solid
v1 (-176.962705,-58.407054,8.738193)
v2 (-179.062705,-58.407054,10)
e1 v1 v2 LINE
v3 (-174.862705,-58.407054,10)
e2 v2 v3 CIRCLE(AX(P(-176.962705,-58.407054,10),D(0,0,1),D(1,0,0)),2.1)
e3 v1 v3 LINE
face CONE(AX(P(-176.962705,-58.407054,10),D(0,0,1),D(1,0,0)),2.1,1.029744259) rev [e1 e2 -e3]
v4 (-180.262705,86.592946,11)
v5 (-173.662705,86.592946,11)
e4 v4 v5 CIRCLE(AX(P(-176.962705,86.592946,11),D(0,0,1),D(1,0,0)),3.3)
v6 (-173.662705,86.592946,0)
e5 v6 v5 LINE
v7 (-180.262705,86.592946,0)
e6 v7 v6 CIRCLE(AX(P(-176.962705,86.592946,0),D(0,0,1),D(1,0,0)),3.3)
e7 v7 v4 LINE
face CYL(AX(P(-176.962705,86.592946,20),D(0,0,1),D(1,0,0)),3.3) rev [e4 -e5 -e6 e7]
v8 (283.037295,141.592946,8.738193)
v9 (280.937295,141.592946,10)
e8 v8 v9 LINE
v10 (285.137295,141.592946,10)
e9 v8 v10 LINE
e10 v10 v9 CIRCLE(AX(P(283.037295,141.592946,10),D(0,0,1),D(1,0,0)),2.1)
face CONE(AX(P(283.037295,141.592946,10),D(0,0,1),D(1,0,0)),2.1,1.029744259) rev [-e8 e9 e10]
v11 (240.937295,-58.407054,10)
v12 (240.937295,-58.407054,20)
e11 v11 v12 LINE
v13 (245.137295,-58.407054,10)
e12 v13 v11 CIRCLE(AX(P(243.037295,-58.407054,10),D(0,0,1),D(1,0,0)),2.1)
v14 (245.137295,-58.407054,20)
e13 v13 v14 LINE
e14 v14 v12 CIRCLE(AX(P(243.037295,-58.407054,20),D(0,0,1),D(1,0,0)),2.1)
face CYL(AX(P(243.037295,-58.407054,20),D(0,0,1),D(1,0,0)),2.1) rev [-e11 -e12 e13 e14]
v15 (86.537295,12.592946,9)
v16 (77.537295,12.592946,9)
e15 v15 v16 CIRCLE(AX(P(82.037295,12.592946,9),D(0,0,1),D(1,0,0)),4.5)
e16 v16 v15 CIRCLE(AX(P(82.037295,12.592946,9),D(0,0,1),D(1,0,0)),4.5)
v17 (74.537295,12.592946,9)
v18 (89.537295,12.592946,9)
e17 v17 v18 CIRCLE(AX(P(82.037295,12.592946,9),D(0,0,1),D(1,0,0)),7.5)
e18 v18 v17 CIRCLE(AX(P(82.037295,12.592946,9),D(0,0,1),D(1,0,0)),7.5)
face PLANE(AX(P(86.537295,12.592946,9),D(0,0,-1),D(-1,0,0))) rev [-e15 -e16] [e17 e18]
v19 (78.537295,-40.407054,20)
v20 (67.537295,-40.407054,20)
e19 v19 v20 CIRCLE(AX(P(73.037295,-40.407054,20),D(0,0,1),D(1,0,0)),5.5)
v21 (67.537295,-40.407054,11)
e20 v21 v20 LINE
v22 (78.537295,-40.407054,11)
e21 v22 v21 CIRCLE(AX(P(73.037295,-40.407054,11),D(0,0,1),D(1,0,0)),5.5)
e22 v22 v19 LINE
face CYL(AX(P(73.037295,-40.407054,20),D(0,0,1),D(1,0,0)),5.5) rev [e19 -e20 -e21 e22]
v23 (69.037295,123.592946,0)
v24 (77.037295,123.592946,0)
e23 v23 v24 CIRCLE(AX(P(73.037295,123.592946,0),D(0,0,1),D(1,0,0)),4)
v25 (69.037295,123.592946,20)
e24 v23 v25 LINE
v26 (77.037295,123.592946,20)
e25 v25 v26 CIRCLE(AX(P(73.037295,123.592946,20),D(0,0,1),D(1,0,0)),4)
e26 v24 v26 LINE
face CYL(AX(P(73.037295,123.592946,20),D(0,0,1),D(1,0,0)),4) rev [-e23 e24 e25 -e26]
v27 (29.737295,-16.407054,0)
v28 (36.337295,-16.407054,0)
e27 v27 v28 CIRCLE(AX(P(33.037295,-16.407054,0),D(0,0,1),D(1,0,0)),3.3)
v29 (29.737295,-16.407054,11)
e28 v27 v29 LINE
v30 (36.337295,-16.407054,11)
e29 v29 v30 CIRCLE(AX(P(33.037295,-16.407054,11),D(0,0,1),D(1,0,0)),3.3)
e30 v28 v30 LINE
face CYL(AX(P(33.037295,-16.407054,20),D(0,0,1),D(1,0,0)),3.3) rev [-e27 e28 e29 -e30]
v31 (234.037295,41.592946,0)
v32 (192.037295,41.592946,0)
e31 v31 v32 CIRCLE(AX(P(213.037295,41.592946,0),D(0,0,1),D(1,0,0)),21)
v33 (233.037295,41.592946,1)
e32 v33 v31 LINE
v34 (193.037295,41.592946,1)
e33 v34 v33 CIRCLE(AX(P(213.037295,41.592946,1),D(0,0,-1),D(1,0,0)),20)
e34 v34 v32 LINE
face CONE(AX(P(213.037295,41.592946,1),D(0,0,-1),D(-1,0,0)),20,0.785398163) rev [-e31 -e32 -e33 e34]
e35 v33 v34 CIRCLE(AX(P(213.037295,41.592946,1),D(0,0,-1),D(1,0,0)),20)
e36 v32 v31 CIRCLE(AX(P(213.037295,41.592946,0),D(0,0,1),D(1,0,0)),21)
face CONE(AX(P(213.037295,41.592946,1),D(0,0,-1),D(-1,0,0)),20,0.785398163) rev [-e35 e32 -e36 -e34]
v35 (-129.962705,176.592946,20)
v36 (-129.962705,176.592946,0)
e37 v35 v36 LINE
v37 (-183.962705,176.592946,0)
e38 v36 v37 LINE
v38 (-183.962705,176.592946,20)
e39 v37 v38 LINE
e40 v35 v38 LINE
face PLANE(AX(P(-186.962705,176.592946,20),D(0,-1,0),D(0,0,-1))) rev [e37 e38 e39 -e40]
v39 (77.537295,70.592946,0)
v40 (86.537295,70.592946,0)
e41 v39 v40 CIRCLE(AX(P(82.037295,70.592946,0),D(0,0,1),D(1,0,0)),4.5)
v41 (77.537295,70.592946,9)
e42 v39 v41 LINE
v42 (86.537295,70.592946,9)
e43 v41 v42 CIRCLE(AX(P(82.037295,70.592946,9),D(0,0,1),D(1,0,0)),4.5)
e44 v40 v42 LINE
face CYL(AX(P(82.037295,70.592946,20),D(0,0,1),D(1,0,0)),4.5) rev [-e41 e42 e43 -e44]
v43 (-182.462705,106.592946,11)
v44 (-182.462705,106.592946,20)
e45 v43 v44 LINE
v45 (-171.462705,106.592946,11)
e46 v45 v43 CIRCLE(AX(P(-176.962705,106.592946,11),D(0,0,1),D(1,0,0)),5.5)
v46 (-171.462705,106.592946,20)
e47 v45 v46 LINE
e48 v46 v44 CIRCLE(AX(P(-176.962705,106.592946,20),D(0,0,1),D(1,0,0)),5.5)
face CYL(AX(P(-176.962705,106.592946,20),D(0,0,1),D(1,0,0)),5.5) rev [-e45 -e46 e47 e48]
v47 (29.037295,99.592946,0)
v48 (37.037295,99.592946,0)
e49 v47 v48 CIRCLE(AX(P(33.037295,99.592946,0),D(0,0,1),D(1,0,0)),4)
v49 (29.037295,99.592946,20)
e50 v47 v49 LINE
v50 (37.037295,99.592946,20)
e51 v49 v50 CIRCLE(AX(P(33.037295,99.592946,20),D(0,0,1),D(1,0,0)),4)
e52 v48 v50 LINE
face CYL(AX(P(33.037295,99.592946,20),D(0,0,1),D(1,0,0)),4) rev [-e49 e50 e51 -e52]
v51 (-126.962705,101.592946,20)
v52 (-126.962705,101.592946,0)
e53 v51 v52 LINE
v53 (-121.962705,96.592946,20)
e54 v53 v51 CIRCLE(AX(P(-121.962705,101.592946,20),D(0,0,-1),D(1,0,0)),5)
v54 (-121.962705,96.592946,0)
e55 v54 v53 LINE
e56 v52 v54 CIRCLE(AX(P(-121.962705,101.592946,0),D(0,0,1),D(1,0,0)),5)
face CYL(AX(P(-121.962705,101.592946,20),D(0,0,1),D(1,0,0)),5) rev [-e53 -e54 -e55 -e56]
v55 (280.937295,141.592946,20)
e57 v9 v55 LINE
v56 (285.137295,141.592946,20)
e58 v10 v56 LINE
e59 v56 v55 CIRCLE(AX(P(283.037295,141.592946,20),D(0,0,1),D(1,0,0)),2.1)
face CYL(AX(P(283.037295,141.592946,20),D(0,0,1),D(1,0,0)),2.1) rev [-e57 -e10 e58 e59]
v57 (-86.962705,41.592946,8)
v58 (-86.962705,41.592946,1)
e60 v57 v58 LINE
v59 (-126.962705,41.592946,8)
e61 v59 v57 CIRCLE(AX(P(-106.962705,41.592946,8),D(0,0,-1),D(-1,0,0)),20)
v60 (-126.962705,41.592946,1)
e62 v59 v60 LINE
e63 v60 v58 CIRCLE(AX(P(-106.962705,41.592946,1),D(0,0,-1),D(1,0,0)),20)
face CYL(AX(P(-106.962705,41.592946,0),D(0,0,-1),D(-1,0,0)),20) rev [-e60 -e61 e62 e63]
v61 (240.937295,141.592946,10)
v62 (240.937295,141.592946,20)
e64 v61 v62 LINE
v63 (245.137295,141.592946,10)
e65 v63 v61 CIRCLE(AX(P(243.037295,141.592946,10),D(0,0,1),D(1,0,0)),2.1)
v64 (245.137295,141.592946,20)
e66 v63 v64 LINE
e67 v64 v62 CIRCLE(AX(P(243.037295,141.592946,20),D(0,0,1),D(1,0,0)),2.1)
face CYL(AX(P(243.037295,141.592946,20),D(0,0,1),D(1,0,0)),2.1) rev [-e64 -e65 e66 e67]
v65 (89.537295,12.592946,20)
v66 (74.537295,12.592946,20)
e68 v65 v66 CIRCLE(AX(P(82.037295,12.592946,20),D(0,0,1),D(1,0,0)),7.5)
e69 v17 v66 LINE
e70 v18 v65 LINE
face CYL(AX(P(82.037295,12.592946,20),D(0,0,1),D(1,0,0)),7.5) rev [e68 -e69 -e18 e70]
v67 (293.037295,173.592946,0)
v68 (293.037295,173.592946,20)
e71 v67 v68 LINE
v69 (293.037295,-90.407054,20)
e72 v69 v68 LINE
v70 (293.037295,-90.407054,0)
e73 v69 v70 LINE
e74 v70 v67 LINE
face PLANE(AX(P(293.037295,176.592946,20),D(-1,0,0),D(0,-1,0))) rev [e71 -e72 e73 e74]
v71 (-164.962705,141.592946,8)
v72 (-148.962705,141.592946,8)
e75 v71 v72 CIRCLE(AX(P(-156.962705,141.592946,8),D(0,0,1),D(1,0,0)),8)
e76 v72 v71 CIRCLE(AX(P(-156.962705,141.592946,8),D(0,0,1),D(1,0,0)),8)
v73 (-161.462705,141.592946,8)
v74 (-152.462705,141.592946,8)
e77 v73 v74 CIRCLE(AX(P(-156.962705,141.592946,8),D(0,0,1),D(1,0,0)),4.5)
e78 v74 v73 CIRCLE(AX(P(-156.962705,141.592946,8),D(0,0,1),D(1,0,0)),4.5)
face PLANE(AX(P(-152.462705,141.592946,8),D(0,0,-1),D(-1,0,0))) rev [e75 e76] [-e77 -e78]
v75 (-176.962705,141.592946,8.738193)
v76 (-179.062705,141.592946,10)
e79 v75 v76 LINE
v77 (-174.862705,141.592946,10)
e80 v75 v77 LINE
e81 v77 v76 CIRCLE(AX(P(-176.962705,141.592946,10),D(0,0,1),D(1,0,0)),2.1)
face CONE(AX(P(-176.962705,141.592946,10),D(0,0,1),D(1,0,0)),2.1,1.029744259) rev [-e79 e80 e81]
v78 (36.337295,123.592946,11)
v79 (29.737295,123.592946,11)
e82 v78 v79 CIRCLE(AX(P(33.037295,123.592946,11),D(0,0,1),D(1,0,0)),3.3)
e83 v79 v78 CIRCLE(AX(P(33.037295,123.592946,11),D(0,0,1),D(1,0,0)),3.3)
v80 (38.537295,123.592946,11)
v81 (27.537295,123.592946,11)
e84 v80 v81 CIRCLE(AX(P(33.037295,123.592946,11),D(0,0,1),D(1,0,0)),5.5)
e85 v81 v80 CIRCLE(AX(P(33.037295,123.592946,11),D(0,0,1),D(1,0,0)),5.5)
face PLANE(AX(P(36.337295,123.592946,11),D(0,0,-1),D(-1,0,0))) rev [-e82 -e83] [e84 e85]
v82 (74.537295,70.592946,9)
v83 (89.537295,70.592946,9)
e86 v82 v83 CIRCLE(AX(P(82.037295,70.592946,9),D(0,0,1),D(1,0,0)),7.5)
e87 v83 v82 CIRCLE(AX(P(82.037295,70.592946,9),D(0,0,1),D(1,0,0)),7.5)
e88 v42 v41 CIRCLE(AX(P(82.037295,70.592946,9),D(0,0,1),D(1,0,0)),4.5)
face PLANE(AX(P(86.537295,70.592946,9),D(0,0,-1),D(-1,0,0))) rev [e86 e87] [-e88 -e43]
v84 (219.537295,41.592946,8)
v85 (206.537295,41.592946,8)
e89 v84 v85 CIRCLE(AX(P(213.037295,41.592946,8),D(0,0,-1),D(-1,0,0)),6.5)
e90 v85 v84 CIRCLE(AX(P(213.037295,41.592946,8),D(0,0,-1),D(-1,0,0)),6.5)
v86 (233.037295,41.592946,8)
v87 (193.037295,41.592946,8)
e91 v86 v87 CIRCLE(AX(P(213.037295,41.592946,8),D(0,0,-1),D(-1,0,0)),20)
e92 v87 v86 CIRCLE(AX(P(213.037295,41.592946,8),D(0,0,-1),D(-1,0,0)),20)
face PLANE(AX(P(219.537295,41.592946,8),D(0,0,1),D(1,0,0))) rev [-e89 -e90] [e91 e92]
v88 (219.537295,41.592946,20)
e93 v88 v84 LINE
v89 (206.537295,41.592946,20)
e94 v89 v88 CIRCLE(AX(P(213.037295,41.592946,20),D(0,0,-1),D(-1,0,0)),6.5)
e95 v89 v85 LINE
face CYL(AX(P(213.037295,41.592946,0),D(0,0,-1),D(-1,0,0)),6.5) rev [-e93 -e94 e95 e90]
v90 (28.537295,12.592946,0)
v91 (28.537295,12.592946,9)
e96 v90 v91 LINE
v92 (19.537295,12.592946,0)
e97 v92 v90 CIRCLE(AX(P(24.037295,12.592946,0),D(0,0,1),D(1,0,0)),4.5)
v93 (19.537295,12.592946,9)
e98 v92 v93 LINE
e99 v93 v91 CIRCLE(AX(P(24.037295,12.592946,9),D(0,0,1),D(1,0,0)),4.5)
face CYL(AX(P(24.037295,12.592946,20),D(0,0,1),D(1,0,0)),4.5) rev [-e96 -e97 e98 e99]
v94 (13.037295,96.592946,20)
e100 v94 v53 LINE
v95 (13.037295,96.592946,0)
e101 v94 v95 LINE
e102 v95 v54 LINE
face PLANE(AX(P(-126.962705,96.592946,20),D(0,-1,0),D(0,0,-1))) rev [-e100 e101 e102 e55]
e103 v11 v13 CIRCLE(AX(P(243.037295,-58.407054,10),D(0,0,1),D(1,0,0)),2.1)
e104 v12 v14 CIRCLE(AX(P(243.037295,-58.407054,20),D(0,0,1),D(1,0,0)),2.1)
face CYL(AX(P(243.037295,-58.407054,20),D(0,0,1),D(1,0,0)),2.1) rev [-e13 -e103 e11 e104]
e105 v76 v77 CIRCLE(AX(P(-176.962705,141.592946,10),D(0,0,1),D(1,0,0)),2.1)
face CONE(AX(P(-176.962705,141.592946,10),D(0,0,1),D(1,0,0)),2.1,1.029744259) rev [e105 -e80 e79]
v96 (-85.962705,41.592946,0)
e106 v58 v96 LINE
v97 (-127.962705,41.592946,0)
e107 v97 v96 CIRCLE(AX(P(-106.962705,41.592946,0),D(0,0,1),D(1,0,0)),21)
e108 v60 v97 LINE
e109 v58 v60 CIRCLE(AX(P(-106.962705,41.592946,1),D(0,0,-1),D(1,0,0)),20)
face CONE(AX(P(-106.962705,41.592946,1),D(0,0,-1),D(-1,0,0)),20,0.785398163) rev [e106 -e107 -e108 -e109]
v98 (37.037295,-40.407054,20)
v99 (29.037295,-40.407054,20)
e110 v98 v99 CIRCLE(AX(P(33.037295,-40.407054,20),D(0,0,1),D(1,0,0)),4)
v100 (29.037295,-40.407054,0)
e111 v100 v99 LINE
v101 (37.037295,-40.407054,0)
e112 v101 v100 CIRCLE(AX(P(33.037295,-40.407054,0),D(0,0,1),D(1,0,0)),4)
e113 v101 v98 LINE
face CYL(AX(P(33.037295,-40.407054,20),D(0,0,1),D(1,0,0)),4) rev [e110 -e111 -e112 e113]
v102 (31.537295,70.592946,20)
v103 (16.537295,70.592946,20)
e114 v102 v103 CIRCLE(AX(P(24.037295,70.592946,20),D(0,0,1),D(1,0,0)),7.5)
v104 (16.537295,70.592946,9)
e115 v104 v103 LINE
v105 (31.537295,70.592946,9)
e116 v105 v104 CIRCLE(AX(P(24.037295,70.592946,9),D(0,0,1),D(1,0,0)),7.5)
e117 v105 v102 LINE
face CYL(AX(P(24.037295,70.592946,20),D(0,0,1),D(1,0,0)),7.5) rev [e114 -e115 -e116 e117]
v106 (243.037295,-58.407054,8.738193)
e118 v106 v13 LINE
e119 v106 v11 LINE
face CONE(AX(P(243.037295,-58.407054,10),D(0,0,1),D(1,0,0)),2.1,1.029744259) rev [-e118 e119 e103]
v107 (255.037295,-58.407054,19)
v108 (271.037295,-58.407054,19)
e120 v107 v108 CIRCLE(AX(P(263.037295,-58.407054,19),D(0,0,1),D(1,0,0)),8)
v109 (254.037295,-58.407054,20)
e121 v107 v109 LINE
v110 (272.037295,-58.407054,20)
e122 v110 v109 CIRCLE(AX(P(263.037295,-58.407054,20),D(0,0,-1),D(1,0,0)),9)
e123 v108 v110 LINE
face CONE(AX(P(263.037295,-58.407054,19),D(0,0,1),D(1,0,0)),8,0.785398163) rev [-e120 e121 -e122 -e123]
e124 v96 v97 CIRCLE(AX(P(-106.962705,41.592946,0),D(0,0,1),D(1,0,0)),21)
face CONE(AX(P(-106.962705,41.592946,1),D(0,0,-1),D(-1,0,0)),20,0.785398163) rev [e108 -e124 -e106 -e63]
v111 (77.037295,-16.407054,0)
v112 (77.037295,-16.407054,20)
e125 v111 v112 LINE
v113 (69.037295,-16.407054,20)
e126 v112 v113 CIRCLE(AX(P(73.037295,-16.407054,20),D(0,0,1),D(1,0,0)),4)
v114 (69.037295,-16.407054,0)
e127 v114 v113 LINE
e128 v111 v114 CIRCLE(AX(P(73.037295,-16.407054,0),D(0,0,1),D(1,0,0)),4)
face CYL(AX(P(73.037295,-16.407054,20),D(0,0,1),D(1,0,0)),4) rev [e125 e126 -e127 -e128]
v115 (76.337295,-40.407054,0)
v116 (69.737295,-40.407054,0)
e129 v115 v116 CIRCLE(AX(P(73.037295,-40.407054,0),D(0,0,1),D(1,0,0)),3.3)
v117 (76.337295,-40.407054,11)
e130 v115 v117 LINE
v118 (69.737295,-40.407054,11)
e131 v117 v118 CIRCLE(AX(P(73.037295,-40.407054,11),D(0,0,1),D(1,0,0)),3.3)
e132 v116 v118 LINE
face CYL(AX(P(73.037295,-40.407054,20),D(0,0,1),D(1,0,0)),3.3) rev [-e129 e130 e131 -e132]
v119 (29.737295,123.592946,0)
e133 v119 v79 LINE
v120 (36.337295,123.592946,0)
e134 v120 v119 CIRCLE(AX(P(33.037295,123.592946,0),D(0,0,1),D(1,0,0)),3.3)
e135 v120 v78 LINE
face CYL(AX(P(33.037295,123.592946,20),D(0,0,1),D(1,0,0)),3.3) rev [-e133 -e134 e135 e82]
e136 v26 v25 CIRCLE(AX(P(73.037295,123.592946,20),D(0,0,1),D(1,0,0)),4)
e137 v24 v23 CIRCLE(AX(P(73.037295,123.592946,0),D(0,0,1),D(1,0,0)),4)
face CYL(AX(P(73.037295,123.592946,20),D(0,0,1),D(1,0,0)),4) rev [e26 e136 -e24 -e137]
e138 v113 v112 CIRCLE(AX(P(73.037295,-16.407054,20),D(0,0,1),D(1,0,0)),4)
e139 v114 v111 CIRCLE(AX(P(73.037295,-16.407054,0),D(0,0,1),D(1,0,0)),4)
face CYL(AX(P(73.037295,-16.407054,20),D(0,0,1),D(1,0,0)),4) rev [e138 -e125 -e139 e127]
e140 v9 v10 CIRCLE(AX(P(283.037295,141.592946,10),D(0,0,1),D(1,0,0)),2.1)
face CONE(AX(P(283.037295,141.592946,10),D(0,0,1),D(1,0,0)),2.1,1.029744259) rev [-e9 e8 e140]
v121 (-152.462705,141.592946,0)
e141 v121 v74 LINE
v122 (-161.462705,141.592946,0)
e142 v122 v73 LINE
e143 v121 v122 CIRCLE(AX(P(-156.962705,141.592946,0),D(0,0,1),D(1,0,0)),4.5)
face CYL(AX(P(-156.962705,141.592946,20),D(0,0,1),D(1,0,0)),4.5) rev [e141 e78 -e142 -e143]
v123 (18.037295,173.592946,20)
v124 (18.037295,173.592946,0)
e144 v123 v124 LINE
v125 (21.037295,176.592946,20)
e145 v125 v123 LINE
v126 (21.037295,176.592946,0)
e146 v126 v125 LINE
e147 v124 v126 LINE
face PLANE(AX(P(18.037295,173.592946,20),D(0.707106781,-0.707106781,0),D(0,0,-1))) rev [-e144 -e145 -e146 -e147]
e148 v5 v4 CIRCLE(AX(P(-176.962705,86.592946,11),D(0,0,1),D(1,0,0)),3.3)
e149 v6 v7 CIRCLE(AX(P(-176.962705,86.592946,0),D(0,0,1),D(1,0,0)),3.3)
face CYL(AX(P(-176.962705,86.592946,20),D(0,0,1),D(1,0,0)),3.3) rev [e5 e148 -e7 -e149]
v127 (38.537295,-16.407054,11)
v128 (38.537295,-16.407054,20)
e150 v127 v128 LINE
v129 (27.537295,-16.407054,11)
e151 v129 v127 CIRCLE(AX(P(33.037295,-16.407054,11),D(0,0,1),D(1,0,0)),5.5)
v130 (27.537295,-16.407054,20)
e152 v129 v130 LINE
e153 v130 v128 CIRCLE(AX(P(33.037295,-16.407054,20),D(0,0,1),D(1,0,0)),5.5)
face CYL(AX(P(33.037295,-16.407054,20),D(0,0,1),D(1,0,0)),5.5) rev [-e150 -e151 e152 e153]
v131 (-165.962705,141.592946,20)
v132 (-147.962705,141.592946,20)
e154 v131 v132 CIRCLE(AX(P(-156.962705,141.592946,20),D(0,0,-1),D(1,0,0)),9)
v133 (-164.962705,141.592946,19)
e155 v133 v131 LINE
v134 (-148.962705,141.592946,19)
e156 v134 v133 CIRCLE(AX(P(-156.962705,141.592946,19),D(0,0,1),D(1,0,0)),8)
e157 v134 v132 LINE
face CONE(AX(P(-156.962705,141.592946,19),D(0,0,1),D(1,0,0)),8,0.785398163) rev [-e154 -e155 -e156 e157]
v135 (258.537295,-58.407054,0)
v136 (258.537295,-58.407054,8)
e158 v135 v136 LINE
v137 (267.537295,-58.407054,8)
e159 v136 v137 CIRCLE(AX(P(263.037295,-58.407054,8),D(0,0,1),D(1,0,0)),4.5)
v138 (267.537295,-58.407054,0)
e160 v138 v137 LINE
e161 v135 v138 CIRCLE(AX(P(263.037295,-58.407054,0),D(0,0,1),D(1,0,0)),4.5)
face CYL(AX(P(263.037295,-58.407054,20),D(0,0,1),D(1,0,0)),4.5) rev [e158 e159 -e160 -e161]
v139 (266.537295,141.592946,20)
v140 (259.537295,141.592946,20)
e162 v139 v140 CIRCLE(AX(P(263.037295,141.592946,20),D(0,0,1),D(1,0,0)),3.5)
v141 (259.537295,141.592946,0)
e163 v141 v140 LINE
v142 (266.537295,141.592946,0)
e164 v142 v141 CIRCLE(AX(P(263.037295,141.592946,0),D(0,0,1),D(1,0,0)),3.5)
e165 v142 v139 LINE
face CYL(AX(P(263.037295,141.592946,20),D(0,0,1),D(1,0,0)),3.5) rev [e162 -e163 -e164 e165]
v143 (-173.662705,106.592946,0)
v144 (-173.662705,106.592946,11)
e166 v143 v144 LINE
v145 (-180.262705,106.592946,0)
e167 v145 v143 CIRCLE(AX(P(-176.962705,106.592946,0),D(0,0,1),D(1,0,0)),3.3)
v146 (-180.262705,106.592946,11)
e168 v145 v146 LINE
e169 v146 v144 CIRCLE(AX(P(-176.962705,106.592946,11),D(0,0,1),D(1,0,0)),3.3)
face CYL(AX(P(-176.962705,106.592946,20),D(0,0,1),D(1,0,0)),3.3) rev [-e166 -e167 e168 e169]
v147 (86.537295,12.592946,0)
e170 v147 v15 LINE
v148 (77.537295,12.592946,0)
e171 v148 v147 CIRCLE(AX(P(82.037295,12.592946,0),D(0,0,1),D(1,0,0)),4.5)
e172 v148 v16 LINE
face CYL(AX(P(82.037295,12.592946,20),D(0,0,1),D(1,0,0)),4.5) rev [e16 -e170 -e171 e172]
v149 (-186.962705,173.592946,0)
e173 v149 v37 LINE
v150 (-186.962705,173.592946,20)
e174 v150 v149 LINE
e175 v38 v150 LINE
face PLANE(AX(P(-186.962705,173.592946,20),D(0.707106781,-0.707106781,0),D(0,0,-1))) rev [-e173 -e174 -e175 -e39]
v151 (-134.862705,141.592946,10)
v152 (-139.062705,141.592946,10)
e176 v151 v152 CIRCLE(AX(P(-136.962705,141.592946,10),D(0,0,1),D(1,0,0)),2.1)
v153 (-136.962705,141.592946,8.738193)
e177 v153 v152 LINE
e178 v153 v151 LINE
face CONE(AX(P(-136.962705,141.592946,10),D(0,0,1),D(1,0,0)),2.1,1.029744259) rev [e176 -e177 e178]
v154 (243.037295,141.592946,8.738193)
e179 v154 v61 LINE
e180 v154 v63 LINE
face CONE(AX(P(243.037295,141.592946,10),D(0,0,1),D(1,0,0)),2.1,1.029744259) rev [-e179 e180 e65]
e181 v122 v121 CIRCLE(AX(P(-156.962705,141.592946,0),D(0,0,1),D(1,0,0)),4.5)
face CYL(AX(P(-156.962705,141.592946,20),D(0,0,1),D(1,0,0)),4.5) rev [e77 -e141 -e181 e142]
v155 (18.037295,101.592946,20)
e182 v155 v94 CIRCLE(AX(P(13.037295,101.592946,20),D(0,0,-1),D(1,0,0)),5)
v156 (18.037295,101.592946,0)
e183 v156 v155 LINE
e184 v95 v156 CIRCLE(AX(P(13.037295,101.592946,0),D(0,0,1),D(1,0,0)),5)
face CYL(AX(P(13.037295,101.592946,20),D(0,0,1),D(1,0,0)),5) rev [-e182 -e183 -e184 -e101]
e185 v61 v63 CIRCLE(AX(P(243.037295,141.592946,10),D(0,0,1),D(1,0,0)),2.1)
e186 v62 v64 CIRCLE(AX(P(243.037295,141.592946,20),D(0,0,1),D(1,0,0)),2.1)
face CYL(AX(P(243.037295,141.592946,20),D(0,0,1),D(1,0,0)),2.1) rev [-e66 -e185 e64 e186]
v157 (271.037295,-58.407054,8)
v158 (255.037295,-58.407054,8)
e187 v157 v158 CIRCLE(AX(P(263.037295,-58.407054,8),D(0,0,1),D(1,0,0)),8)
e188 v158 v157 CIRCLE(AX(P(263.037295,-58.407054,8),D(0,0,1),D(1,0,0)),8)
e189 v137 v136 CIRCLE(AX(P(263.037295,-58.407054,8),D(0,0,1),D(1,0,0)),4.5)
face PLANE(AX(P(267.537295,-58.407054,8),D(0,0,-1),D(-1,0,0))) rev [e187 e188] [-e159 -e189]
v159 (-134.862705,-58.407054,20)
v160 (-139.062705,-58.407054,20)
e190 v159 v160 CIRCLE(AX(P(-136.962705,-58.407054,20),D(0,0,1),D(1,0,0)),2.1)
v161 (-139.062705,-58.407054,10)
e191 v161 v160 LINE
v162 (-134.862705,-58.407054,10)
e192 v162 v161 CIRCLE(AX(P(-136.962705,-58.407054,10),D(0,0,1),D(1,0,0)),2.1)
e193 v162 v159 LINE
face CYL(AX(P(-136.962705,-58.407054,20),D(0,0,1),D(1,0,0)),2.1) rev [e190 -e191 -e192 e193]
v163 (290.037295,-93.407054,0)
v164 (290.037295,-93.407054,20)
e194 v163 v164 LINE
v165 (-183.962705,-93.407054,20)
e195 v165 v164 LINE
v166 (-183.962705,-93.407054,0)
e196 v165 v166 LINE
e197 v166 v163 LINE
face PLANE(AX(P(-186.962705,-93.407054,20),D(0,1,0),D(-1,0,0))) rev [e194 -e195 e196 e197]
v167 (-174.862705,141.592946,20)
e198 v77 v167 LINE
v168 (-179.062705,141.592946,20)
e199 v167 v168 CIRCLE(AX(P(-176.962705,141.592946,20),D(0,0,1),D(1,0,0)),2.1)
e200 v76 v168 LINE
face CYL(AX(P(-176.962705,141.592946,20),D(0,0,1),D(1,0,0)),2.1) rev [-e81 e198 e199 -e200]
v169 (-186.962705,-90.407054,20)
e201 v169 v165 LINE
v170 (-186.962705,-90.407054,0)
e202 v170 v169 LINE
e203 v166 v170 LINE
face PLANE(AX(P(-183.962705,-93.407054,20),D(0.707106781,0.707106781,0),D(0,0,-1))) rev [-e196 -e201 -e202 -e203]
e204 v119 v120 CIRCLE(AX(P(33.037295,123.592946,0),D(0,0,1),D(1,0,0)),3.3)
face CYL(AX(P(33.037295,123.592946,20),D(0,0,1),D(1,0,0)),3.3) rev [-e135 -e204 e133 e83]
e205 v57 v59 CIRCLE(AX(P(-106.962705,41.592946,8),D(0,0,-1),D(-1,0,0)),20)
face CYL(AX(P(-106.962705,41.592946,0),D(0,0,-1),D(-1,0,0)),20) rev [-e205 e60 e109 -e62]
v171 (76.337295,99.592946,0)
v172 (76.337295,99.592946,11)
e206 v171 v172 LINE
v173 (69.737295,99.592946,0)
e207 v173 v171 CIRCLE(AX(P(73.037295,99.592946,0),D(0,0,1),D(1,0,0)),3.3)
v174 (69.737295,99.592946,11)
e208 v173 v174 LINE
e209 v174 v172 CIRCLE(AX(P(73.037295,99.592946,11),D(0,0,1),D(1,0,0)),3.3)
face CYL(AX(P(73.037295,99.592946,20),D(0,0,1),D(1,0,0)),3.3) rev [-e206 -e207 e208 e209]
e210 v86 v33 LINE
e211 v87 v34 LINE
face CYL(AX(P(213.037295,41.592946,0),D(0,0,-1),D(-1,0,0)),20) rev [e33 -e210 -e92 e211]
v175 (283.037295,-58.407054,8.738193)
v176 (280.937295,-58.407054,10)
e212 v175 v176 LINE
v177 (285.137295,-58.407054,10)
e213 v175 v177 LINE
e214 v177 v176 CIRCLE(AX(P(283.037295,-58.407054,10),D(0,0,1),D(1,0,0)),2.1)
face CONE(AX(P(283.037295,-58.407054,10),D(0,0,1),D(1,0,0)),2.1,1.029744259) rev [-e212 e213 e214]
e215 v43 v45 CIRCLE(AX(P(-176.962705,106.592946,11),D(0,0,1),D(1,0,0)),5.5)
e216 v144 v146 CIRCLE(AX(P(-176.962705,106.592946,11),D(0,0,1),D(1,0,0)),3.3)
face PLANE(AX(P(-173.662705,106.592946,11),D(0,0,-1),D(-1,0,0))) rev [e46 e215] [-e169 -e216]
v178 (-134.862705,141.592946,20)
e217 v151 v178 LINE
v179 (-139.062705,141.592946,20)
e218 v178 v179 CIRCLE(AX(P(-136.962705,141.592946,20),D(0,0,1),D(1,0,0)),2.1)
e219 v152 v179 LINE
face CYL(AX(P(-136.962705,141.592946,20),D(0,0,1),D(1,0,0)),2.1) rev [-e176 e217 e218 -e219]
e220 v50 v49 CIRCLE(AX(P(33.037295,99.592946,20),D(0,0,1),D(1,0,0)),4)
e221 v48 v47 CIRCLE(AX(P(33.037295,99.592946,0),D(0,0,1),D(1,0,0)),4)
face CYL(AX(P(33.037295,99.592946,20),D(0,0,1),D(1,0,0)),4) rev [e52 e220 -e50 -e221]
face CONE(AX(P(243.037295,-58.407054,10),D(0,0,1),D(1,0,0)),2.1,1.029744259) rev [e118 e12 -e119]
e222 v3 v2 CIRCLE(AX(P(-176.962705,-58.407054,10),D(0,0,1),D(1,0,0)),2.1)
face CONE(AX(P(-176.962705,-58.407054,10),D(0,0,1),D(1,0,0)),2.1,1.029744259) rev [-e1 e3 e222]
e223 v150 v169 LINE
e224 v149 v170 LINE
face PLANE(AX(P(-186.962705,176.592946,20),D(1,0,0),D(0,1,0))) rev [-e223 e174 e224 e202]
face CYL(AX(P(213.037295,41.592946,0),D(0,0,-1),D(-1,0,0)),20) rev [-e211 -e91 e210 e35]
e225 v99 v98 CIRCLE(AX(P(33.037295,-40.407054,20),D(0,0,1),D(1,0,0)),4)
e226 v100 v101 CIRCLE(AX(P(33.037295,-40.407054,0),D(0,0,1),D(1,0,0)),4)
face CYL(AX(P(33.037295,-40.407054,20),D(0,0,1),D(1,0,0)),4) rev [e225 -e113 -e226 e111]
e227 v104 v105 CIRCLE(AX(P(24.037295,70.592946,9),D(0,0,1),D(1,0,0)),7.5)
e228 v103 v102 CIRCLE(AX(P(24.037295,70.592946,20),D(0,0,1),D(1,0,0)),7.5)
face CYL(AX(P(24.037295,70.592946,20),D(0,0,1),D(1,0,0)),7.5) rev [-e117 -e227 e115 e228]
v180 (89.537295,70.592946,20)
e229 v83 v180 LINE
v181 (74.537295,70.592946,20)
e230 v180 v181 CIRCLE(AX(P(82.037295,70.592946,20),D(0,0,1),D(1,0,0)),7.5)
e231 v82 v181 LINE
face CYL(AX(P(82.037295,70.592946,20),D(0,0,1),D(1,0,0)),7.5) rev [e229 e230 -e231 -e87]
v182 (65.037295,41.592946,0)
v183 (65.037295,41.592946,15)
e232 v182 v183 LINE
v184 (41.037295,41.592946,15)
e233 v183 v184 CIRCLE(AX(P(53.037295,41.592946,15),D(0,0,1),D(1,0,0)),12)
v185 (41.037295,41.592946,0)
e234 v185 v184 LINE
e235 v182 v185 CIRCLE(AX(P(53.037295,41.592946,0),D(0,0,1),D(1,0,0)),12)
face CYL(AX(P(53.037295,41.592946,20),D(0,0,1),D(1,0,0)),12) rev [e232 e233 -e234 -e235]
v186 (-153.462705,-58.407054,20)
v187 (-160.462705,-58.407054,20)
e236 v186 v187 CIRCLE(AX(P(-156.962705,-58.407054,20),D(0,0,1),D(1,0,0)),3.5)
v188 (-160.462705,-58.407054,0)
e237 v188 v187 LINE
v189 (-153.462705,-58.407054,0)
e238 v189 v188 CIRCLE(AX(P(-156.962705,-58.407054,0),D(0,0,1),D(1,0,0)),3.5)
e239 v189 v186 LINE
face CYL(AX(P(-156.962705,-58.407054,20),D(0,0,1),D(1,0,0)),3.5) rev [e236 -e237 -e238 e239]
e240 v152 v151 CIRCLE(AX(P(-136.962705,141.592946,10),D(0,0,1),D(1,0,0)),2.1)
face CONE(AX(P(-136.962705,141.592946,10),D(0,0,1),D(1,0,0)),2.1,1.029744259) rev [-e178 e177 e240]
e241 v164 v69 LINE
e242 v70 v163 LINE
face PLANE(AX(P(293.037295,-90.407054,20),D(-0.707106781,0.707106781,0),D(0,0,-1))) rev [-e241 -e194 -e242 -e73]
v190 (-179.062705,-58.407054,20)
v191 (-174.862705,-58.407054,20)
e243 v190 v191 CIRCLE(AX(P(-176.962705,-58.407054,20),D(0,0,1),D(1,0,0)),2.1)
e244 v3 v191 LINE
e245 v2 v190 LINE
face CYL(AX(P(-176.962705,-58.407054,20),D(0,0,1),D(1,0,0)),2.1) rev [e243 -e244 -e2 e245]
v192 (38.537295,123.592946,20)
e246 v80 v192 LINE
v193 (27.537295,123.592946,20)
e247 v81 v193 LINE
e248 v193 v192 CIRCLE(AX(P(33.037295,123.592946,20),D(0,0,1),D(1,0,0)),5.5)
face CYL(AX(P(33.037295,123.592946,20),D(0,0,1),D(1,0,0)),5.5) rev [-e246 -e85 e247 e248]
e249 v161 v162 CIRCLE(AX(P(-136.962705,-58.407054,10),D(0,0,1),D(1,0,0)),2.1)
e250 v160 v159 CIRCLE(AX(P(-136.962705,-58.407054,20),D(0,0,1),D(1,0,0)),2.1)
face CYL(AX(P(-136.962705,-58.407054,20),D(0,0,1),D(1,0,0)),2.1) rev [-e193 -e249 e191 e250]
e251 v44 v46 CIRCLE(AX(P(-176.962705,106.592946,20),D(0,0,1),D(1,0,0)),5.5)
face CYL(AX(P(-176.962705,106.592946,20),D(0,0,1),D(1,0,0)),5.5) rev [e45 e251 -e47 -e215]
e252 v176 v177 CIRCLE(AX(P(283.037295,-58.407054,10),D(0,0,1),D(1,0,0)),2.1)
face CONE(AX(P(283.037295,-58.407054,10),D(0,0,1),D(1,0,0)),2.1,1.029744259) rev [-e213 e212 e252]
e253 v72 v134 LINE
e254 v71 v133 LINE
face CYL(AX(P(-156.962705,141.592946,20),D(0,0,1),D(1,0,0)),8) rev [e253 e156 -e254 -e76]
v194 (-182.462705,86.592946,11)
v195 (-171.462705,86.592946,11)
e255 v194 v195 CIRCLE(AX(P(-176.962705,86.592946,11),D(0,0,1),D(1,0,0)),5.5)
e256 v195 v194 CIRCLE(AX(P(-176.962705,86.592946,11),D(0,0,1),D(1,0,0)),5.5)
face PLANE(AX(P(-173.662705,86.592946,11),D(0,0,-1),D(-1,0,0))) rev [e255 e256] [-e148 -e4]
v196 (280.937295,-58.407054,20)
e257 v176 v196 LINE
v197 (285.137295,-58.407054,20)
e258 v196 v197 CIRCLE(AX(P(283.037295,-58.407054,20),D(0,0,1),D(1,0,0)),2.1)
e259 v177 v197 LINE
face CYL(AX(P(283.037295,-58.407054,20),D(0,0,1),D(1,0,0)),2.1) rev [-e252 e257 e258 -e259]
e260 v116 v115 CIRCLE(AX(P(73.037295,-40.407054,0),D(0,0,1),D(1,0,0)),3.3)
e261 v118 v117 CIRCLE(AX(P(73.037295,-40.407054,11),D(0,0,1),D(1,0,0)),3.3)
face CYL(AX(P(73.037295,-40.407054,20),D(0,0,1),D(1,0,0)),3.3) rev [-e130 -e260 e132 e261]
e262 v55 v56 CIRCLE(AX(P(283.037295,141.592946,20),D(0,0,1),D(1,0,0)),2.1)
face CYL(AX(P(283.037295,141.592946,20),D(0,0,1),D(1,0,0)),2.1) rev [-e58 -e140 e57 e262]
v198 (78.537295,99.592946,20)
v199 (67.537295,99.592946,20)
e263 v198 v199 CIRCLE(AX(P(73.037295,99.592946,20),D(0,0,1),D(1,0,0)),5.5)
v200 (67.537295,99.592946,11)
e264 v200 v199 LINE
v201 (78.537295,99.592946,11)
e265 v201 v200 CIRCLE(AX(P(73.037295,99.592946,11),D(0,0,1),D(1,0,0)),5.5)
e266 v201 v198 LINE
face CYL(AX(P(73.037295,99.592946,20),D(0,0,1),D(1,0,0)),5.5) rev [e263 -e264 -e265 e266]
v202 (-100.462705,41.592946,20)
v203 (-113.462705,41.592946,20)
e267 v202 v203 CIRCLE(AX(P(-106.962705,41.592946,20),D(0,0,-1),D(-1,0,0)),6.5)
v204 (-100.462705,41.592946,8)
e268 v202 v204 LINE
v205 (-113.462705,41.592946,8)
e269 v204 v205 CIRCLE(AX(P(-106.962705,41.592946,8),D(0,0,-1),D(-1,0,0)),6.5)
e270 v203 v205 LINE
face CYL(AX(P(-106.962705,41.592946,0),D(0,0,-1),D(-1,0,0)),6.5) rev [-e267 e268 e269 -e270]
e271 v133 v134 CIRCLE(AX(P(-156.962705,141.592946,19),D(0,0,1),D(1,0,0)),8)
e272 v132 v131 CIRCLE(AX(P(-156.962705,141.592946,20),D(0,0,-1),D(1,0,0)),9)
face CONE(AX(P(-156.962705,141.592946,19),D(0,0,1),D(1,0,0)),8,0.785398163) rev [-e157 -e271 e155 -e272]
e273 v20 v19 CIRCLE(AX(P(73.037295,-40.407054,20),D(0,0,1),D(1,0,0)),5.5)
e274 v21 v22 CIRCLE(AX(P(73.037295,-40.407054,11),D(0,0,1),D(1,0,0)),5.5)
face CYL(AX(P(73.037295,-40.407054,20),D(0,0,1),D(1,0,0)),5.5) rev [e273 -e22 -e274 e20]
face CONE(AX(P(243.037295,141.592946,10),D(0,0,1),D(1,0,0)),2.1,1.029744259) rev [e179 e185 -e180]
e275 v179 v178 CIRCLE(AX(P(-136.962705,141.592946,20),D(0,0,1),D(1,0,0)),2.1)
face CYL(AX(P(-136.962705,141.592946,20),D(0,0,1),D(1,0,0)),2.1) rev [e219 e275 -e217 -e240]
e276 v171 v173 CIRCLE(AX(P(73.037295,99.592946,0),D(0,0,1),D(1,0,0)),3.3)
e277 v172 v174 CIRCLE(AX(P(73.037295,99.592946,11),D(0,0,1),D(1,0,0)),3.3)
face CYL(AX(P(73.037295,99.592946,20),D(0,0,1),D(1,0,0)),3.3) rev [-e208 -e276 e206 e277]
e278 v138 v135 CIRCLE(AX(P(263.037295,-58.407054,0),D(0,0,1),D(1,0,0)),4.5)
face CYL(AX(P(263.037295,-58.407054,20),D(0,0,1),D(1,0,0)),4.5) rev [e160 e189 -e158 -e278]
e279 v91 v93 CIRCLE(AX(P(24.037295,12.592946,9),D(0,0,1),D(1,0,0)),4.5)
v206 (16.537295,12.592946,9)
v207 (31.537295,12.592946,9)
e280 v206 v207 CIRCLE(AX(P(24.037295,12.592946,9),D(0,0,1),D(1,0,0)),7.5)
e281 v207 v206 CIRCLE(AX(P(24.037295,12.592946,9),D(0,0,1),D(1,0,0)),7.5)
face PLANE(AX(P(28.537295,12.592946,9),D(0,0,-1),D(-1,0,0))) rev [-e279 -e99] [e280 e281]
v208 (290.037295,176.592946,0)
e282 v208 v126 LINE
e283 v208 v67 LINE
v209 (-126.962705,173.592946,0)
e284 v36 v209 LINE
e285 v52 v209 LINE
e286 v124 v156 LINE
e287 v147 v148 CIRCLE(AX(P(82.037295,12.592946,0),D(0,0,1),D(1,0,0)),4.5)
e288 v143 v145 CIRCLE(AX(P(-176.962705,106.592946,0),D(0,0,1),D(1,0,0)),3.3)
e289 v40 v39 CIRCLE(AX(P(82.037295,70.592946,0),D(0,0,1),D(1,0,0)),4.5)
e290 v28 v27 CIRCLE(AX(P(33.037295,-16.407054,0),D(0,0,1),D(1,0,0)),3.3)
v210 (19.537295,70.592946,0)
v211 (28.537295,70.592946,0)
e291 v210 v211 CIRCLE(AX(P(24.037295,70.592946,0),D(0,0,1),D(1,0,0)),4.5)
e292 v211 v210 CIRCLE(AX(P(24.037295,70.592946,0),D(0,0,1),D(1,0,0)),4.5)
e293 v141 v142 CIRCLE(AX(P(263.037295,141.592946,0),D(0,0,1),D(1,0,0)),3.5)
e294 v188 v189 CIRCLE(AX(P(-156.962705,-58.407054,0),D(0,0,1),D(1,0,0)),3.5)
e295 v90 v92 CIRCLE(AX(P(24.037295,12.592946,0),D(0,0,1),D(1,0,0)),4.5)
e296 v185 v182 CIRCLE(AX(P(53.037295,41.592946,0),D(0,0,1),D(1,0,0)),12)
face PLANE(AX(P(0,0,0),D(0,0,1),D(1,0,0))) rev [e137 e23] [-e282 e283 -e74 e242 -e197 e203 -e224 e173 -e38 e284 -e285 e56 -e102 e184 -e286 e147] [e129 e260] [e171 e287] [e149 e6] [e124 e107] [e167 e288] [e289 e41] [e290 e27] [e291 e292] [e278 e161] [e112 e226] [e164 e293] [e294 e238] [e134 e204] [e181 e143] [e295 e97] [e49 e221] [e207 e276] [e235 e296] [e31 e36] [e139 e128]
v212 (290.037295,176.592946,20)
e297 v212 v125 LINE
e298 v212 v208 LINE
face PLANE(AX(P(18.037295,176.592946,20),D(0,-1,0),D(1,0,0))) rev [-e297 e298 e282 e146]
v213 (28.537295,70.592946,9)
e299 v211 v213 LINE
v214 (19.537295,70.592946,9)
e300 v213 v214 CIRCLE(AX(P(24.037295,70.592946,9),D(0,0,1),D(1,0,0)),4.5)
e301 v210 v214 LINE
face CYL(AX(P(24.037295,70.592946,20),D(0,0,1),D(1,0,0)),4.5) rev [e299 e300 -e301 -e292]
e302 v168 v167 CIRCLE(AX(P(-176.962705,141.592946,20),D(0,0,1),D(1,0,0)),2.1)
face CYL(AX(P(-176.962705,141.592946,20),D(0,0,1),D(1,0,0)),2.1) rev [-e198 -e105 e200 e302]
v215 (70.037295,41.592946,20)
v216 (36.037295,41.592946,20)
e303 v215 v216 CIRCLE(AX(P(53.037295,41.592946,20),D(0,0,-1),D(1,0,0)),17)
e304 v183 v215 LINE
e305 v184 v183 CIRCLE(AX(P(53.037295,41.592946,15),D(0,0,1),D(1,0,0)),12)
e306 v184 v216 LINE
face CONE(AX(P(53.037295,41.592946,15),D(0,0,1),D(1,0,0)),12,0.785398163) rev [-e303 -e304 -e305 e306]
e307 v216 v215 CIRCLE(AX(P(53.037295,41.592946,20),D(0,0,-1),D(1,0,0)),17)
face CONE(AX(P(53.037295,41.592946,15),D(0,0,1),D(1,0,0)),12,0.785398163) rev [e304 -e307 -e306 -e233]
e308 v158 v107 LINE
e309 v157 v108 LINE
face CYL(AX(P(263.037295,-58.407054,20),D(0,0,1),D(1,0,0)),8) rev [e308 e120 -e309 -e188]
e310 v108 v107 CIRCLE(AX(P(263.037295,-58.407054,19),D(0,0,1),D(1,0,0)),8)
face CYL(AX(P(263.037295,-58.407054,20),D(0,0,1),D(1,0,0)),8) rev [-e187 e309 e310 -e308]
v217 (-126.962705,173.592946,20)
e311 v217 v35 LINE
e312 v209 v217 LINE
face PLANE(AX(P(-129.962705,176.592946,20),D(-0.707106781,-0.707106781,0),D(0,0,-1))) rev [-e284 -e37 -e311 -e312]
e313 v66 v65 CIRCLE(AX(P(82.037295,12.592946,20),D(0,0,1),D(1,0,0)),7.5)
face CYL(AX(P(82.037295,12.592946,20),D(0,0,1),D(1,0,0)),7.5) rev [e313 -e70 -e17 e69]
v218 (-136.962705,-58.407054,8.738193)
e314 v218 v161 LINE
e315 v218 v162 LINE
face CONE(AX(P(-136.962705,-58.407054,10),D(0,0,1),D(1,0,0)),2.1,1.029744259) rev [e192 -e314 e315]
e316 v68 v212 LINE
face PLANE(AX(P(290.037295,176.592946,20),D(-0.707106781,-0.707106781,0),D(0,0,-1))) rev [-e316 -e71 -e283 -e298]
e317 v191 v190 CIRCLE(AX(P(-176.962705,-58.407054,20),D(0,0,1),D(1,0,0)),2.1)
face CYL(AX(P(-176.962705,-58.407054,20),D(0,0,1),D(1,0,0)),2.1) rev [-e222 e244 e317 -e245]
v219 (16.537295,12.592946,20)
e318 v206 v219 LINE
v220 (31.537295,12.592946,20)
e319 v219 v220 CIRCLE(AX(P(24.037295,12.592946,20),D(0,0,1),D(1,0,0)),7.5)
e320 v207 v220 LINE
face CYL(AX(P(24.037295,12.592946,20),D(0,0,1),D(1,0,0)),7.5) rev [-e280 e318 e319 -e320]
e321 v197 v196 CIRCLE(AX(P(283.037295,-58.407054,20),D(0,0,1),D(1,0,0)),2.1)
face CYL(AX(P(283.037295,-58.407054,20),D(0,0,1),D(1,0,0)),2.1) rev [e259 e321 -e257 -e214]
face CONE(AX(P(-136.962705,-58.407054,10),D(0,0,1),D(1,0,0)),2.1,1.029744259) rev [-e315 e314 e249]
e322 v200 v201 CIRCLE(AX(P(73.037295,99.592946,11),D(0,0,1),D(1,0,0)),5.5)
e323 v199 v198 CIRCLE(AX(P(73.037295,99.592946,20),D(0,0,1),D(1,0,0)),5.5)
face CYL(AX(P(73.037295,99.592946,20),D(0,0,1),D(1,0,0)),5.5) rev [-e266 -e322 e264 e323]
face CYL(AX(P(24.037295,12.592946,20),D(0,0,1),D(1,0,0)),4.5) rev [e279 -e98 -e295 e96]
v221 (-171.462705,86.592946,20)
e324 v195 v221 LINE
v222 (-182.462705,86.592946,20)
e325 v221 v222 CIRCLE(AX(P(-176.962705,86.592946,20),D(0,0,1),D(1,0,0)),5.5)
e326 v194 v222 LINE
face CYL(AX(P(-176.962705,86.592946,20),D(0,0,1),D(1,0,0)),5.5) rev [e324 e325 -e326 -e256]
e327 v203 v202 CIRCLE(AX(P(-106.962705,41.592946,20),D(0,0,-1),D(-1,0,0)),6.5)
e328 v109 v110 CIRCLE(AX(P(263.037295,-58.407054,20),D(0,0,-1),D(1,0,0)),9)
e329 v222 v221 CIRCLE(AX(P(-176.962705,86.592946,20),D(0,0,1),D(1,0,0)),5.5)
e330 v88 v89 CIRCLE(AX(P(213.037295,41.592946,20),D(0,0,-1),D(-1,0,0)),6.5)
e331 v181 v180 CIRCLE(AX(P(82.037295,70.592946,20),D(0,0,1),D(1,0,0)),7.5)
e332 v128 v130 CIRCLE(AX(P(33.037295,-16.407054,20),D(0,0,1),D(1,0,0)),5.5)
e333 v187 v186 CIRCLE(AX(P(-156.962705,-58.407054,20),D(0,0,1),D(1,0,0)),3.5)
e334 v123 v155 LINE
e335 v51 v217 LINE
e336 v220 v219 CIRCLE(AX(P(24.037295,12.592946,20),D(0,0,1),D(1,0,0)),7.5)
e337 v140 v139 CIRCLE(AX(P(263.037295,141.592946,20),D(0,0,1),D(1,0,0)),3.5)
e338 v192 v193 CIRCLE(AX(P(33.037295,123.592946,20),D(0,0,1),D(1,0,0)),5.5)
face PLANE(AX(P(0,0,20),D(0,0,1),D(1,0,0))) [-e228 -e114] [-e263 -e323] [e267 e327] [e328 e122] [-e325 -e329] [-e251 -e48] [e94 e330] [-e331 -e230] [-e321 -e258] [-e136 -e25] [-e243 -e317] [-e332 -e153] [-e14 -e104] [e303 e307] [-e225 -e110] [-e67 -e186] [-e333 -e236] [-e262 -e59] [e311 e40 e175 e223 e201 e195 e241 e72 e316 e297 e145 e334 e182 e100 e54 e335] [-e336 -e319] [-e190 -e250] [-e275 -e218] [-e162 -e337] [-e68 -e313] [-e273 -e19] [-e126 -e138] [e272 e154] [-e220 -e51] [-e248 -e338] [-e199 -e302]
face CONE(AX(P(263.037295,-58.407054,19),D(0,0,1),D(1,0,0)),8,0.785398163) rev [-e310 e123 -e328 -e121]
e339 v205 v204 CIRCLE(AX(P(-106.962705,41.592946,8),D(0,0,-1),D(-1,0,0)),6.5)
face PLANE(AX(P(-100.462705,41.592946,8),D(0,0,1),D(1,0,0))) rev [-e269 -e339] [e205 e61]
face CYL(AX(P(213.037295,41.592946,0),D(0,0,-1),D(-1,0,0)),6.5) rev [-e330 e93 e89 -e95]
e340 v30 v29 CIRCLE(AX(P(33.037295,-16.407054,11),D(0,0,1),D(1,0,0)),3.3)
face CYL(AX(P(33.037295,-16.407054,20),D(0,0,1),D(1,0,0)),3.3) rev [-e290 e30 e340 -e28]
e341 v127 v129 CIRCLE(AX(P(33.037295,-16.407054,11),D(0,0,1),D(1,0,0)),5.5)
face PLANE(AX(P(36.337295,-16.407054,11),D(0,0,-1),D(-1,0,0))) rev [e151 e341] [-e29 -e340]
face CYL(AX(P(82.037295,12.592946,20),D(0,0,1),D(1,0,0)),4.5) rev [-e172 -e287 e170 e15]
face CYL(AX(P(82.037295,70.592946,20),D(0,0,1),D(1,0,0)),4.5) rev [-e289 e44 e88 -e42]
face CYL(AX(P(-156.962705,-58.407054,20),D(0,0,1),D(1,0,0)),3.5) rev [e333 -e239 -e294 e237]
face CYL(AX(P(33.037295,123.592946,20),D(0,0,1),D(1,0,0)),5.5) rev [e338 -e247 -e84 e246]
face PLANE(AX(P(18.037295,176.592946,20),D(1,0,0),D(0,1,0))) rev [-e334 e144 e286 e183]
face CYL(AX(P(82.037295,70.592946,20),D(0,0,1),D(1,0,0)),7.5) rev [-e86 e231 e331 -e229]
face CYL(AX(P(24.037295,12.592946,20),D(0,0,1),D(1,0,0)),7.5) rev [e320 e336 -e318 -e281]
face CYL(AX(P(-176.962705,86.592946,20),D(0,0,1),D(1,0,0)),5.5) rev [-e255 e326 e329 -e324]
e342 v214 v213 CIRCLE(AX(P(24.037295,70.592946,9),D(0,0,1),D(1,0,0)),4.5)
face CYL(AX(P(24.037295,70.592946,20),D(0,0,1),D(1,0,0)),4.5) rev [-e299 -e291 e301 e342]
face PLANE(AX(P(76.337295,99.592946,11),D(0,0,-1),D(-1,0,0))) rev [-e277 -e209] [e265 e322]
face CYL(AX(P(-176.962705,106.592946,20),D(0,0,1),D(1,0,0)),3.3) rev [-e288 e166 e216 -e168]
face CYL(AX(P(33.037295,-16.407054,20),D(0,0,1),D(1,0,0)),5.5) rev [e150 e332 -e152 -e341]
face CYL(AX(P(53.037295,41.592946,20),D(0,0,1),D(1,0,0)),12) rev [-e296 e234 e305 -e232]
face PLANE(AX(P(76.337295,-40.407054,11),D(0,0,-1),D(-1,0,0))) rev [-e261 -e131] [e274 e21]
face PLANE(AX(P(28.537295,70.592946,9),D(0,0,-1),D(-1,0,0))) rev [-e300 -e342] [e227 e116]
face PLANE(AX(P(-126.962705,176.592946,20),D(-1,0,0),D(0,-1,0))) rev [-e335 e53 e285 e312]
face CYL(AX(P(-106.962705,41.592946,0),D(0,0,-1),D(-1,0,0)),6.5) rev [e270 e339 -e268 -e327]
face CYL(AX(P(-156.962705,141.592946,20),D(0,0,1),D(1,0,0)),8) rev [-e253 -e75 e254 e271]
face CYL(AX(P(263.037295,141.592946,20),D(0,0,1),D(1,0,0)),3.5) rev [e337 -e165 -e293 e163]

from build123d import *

# Parameters (mm, degrees)
BOSS_EXTRUDE1_DEPTH   = 20
FILLET1_R             = 5
CHAMFER1_SIZE         = 3
HOLE2_D               = 6.6
HOLE2_CBORE_D         = 11
HOLE2_CBORE_DEPTH     = 9
M5_TAPPED_HOLE1_D     = 4.2
M5_TAPPED_HOLE1_DEPTH = 10
M5_TAPPED_HOLE1_TIP   = 1.2618073
M8X1_0_TAPPED_HOLE1_D = 7
HOLE3_D               = 9
HOLE3_CBORE_D         = 16
HOLE3_CBORE_DEPTH     = 12
HOLE4_D               = 9
HOLE4_CBORE_D         = 15
HOLE4_CBORE_DEPTH     = 11
HOLE5_D               = 6.6
HOLE5_CBORE_D         = 11
HOLE5_CBORE_DEPTH     = 9
HOLE6_D               = 8
HOLE7_D               = 24
HOLE8_D               = 13
HOLE8_CBORE_D         = 40
HOLE8_CBORE_DEPTH     = 8
CHAMFER2_SIZE         = 1
CHAMFER3_SIZE         = 5


with BuildPart() as part:
    # Sketch1 → Boss-Extrude1 (new body)
    with BuildSketch(Plane.XY):
        Polygon((18.037295083, 176.592946031), (293.037295083, 176.592946031), (293.037295083, -93.407053969), (-186.962704917, -93.407053969), (-186.962704917, 176.592946031), (-126.962704917, 176.592946031), (-126.962704917, 96.592946031), (18.037295083, 96.592946031), align=None)
    extrude(amount=BOSS_EXTRUDE1_DEPTH)

    # Fillet1
    fillet1_edges = [part.edges().sort_by_distance(p)[0] for p in [
        (-126.962704917, 96.592946031, 10),
        (18.037295083, 96.592946031, 10),
    ]]
    fillet(fillet1_edges, radius=FILLET1_R)

    # Chamfer1
    chamfer1_edges = [part.edges().sort_by_distance(p)[0] for p in [
        (-186.962704917, 176.592946031, 10),
        (-126.962704917, 176.592946031, 10),
        (18.037295083, 176.592946031, 10),
        (293.037295083, 176.592946031, 10),
        (293.037295083, -93.407053969, 10),
        (-186.962704917, -93.407053969, 10),
    ]]
    chamfer(chamfer1_edges, length=CHAMFER1_SIZE)

    # Hole2 (through all)
    with Locations(Plane.XY.offset(20)):
        with Locations((-176.962704917, 106.592946031), (-176.962704917, 86.592946031)):
            CounterBoreHole(HOLE2_D / 2, HOLE2_CBORE_D / 2, HOLE2_CBORE_DEPTH)

    # M5 Tapped Hole1
    with Locations(Plane.XY.offset(20)):
        with Locations((-176.962704917, 141.592946031), (-136.962704917, 141.592946031), (-176.962704917, -58.407053969), (-136.962704917, -58.407053969), (243.037295083, -58.407053969), (283.037295083, -58.407053969), (283.037295083, 141.592946031), (243.037295083, 141.592946031)):
            Hole(M5_TAPPED_HOLE1_D / 2, depth=M5_TAPPED_HOLE1_DEPTH)
            with Locations((0, 0, -(M5_TAPPED_HOLE1_DEPTH + M5_TAPPED_HOLE1_TIP / 2))):  # 118° drill point
                Cone(0, M5_TAPPED_HOLE1_D / 2, M5_TAPPED_HOLE1_TIP, mode=Mode.SUBTRACT)

    # M8x1.0 Tapped Hole1 (through all)
    with Locations(Plane.XY.offset(20)):
        with Locations((-156.962704917, -58.407053969), (263.037295083, 141.592946031)):
            Hole(M8X1_0_TAPPED_HOLE1_D / 2)

    # Hole3 (through all)
    with Locations(Plane.XY.offset(20)):
        with Locations((-156.962704917, 141.592946031), (263.037295083, -58.407053969)):
            CounterBoreHole(HOLE3_D / 2, HOLE3_CBORE_D / 2, HOLE3_CBORE_DEPTH)

    # Hole4 (through all)
    with Locations(Plane.XY.offset(20)):
        with Locations((24.037295083, 70.592946031), (82.037295083, 70.592946031), (82.037295083, 12.592946031), (24.037295083, 12.592946031)):
            CounterBoreHole(HOLE4_D / 2, HOLE4_CBORE_D / 2, HOLE4_CBORE_DEPTH)

    # Hole5 (through all)
    with Locations(Plane.XY.offset(20)):
        with Locations((33.037295083, 123.592946031), (73.037295083, 99.592946031), (33.037295083, -16.407053969), (73.037295083, -40.407053969)):
            CounterBoreHole(HOLE5_D / 2, HOLE5_CBORE_D / 2, HOLE5_CBORE_DEPTH)

    # Hole6 (through all)
    with Locations(Plane.XY.offset(20)):
        with Locations((73.037295083, 123.592946031), (33.037295083, 99.592946031), (33.037295083, -40.407053969), (73.037295083, -16.407053969)):
            Hole(HOLE6_D / 2)

    # Hole7 (through all)
    with Locations(Plane.XY.offset(20)):
        with Locations((53.037295083, 41.592946031)):
            Hole(HOLE7_D / 2)

    # Hole8 (through all)
    with Locations(Plane(origin=(0, 0, 0), x_dir=(-1, 0, 0), z_dir=(0, 0, -1))):
        with Locations((-213.037295083, 41.592946031), (106.962704917, 41.592946031)):
            CounterBoreHole(HOLE8_D / 2, HOLE8_CBORE_D / 2, HOLE8_CBORE_DEPTH)

    # Chamfer2
    chamfer2_edges = [part.edges().sort_by_distance(p)[0] for p in [
        (255.037295083, -58.407053969, 20),
        (-164.962704917, 141.592946031, 20),
        (-86.962704917, 41.592946031, 0),
        (233.037295083, 41.592946031, 0),
    ]]
    chamfer(chamfer2_edges, length=CHAMFER2_SIZE)

    # Chamfer3
    chamfer3_edges = [part.edges().sort_by_distance(p)[0] for p in [
        (65.037295083, 41.592946031, 20),
    ]]
    chamfer(chamfer3_edges, length=CHAMFER3_SIZE)


solid = part.part
